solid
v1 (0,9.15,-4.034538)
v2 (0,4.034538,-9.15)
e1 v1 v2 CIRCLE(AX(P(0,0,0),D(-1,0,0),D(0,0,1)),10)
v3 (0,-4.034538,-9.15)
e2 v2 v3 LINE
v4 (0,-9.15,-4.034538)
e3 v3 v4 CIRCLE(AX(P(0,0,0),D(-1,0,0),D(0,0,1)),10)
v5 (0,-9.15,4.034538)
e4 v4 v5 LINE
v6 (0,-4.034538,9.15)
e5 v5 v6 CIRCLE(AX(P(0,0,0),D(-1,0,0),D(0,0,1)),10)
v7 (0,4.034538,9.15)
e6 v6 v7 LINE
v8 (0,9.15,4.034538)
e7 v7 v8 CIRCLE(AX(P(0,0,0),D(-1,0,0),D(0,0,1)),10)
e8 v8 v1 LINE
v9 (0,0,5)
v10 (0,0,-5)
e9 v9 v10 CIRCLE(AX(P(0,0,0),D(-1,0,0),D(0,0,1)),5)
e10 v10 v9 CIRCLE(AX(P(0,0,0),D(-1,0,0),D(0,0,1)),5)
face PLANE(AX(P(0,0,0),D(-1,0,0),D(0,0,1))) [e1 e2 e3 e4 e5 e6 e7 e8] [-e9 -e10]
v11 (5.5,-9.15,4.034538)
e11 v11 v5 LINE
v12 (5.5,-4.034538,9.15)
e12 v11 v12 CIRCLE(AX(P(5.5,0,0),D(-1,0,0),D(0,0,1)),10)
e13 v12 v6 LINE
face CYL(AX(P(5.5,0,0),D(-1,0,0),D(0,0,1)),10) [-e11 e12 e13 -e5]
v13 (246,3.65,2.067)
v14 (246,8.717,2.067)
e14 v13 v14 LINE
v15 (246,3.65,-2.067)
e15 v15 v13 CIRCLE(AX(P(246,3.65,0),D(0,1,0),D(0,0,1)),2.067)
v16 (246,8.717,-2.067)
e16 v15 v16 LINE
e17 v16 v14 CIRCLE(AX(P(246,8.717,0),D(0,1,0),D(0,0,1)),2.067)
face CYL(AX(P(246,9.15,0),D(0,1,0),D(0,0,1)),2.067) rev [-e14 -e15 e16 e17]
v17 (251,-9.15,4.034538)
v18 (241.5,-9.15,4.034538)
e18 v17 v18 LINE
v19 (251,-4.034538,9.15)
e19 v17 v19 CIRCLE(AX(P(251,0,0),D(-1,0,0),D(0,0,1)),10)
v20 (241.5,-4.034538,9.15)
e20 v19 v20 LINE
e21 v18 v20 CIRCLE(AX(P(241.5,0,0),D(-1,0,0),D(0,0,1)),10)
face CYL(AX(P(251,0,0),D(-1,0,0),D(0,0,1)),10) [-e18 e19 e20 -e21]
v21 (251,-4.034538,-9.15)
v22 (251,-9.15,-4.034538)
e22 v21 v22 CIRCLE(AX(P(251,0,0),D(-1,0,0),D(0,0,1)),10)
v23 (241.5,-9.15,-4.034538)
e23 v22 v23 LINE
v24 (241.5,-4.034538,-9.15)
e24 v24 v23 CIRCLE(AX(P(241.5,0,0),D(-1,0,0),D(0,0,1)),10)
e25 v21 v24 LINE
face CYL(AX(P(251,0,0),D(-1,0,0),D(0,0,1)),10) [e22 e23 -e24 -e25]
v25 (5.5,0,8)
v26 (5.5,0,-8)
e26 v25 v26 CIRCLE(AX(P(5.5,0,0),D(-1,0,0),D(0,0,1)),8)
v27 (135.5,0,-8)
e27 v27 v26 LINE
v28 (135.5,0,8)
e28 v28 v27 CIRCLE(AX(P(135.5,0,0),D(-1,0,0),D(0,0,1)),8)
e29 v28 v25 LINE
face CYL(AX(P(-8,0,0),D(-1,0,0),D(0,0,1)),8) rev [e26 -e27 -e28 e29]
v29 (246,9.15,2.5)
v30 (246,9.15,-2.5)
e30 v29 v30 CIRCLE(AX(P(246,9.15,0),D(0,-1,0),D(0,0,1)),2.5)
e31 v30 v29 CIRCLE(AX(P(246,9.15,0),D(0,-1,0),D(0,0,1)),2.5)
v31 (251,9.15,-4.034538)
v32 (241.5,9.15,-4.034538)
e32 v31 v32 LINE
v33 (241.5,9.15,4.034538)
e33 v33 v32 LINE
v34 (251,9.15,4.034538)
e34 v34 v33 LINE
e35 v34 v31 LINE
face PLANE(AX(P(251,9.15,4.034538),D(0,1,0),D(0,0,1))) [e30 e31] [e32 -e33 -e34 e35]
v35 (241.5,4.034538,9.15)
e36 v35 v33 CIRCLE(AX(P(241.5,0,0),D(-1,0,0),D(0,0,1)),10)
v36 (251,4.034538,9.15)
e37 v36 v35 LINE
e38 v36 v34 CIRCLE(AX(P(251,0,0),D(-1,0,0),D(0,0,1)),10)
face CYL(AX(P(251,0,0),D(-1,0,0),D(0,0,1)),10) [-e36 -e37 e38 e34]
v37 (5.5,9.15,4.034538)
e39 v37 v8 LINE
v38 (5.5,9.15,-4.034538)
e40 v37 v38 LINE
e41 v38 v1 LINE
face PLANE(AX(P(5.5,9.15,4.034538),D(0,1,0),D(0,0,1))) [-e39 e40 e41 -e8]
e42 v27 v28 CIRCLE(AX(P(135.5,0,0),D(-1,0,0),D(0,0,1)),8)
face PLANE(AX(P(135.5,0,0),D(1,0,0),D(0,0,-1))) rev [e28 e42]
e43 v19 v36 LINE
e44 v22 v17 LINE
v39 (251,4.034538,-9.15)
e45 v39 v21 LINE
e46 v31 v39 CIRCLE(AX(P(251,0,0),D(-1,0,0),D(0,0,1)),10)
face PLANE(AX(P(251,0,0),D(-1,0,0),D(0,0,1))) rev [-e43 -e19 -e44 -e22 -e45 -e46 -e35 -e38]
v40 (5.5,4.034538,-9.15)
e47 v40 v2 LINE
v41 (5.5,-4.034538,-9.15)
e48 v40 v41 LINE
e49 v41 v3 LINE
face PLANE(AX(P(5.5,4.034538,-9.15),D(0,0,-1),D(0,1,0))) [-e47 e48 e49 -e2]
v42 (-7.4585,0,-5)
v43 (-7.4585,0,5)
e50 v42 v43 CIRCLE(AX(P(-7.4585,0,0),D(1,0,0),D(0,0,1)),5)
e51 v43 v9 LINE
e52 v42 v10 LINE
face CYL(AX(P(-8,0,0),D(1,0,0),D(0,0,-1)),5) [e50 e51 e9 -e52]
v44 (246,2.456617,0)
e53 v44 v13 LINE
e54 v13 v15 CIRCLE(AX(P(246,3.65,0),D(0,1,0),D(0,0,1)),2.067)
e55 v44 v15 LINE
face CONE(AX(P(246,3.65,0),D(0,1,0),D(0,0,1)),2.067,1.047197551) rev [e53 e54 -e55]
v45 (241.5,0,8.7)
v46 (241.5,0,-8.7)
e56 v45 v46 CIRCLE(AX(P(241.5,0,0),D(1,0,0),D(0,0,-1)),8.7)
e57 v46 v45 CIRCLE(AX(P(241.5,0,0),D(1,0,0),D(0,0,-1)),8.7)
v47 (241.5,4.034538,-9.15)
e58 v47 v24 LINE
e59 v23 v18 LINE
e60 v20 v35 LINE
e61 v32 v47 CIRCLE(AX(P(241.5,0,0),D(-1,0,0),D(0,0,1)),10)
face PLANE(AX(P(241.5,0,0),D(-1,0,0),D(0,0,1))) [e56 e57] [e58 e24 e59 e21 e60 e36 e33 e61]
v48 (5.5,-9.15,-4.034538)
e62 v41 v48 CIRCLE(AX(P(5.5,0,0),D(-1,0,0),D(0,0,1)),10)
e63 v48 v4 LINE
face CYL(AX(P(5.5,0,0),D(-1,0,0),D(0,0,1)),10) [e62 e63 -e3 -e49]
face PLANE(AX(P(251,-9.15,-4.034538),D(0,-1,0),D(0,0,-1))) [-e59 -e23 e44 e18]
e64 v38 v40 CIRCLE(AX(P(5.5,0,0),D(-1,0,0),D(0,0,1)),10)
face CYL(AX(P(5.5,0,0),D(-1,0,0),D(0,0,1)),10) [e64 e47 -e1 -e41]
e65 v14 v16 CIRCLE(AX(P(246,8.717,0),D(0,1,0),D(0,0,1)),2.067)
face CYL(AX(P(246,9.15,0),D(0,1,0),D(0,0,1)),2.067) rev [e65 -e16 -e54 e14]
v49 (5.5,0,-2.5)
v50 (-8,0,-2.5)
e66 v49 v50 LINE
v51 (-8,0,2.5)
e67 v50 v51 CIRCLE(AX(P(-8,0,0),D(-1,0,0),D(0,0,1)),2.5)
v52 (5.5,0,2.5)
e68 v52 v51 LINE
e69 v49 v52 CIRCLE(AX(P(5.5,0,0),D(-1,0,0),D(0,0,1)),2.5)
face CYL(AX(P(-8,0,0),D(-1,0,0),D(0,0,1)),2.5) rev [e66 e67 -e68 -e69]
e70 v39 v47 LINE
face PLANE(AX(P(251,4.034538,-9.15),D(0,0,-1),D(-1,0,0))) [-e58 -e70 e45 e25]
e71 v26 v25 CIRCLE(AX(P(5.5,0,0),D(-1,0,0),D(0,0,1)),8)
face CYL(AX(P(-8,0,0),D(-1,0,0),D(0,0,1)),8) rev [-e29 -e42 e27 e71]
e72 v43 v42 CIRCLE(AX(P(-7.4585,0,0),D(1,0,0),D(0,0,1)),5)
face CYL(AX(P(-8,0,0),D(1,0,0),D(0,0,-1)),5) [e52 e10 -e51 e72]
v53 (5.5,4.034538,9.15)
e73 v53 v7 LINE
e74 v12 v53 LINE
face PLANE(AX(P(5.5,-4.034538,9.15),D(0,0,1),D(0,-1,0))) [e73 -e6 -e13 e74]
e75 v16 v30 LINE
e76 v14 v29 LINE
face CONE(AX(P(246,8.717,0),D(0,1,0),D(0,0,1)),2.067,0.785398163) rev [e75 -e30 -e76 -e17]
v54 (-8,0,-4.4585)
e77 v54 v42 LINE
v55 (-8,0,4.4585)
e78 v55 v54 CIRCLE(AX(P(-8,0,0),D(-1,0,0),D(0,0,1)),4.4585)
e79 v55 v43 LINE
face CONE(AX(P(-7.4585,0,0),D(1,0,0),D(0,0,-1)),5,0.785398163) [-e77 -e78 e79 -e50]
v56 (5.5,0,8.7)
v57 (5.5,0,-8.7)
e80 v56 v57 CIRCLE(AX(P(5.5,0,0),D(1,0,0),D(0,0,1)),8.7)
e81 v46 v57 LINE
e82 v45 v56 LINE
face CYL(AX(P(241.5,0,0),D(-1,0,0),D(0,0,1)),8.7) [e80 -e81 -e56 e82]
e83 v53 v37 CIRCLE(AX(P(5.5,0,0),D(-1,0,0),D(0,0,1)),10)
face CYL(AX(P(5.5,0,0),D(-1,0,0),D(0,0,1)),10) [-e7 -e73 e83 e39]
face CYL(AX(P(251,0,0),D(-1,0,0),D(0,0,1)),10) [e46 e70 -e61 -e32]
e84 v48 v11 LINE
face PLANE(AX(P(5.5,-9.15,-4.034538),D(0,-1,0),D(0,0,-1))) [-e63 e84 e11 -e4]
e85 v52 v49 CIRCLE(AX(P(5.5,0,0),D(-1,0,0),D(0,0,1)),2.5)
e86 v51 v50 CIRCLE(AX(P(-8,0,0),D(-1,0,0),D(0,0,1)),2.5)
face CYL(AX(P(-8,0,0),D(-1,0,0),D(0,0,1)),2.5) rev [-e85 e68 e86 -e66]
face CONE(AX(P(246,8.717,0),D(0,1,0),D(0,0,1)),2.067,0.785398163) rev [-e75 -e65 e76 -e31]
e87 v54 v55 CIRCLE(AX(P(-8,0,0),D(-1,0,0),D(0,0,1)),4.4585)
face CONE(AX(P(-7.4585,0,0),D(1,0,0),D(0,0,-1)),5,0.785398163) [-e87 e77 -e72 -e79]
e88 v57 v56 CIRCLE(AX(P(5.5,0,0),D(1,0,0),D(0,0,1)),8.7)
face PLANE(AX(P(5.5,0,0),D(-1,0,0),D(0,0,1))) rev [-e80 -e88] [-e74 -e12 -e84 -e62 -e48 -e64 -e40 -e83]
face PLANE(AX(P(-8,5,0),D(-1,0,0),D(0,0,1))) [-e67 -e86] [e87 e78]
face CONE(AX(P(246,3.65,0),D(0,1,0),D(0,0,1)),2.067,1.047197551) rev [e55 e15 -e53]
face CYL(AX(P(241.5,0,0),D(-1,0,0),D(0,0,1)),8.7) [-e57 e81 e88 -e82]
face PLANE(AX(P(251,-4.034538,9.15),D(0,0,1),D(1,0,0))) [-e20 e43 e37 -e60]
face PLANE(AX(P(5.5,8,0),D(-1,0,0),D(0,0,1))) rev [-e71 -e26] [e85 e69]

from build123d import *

# Parameters (mm, degrees)
BOSS_EXTRUDE1_DEPTH        = 5.5
SKETCH2_R                  = 8.7
BOSS_EXTRUDE2_DEPTH        = 236
BOSS_EXTRUDE3_DEPTH        = 9.5
SKETCH4_W                  = 8
SKETCH4_H                  = 5
M3_5_CLEARANCE_HOLE1_D     = 4.134
M3_5_CLEARANCE_HOLE1_DEPTH = 5.5
M3_5_CLEARANCE_HOLE1_TIP   = 1.193383006
CHAMFER1_SIZE              = 0.5415
CHAMFER2_SIZE              = 0.433


with BuildPart() as part:
    # Sketch1 → Boss-Extrude1 (new body)
    with BuildSketch(Plane(origin=(0, 0, 0), x_dir=(0, -1, 0), z_dir=(-1, 0, 0))):
        with BuildLine():
            Line((4.034538387, 9.15), (-4.034538387, 9.15))
            ThreePointArc((-4.034538387, 9.15), (-7.071067812, 7.071067812), (-9.15, 4.034538387))
            Line((-9.15, 4.034538387), (-9.15, -4.034538387))
            ThreePointArc((-9.15, -4.034538387), (-7.071067812, -7.071067812), (-4.034538387, -9.15))
            Line((-4.034538387, -9.15), (4.034538387, -9.15))
            ThreePointArc((4.034538387, -9.15), (7.071067812, -7.071067812), (9.15, -4.034538387))
            Line((9.15, -4.034538387), (9.15, 4.034538387))
            ThreePointArc((9.15, 4.034538387), (7.071067812, 7.071067812), (4.034538387, 9.15))
        make_face()
    extrude(amount=-BOSS_EXTRUDE1_DEPTH)

    # Sketch2 → Boss-Extrude2 (add)
    with BuildSketch(Plane(origin=(5.5, 0, 0), x_dir=(0, 0, -1), z_dir=(1, 0, 0))):
        with Locations(Location((0, 0, 0), (0, 0, 180))):
            Circle(SKETCH2_R)
    extrude(amount=BOSS_EXTRUDE2_DEPTH)

    # Sketch3 → Boss-Extrude3 (add)
    with BuildSketch(Plane(origin=(241.5, 0, 0), x_dir=(0, -1, 0), z_dir=(-1, 0, 0))):
        with BuildLine():
            Line((-9.15, 4.034538387), (-9.15, -4.034538387))
            ThreePointArc((-9.15, -4.034538387), (-7.071067812, -7.071067812), (-4.034538387, -9.15))
            Line((-4.034538387, -9.15), (4.034538387, -9.15))
            ThreePointArc((4.034538387, -9.15), (7.071067812, -7.071067812), (9.15, -4.034538387))
            Line((9.15, -4.034538387), (9.15, 4.034538387))
            ThreePointArc((9.15, 4.034538387), (7.071067812, 7.071067812), (4.034538387, 9.15))
            Line((4.034538387, 9.15), (-4.034538387, 9.15))
            ThreePointArc((-4.034538387, 9.15), (-7.071067812, 7.071067812), (-9.15, 4.034538387))
        make_face()
    extrude(amount=-BOSS_EXTRUDE3_DEPTH)

    # Sketch4 → Revolve1 (revolve)
    with BuildSketch(Plane.XY, mode=Mode.PRIVATE) as revolve1_sk:
        with Locations((-4, 2.5)):
            Rectangle(SKETCH4_W, SKETCH4_H)
    revolve(revolve1_sk.sketch.rotate(Axis((-8, 0, 0), (1, 0, 0)), 270), axis=Axis((-8, 0, 0), (1, 0, 0)))

    # M3.5 Clearance Hole1
    with Locations(Plane(origin=(0, 9.15, 0), x_dir=(1, 0, 0), z_dir=(0, 1, 0))):
        with Locations((246, 0)):
            Hole(M3_5_CLEARANCE_HOLE1_D / 2, depth=M3_5_CLEARANCE_HOLE1_DEPTH)
            with Locations((0, 0, -(M3_5_CLEARANCE_HOLE1_DEPTH + M3_5_CLEARANCE_HOLE1_TIP / 2))):  # 120° drill point
                Cone(0, M3_5_CLEARANCE_HOLE1_D / 2, M3_5_CLEARANCE_HOLE1_TIP, mode=Mode.SUBTRACT)

    # Sketch7 → CBORE for M13 SHSS1 (revolve, cut)
    with BuildSketch(Plane(origin=(-8, 0, 0), x_dir=(0, 0, 1), z_dir=(0, 1, 0))):
        Polygon((0, 0), (0, 143.5), (8, 143.5), (8, 13.5), (2.5, 13.5), (2.5, 0), align=None)
    revolve(axis=Axis((-14.35, 0, 0), (1, 0, 0)), mode=Mode.SUBTRACT)

    # Chamfer1
    chamfer1_edges = [part.edges().sort_by_distance(p)[0] for p in [
        (-8, 0, 5),
    ]]
    chamfer(chamfer1_edges, length=CHAMFER1_SIZE)

    # Chamfer2
    chamfer2_edges = [part.edges().sort_by_distance(p)[0] for p in [
        (248.067, 9.15, 0),
    ]]
    chamfer(chamfer2_edges, length=CHAMFER2_SIZE)


solid = part.part
